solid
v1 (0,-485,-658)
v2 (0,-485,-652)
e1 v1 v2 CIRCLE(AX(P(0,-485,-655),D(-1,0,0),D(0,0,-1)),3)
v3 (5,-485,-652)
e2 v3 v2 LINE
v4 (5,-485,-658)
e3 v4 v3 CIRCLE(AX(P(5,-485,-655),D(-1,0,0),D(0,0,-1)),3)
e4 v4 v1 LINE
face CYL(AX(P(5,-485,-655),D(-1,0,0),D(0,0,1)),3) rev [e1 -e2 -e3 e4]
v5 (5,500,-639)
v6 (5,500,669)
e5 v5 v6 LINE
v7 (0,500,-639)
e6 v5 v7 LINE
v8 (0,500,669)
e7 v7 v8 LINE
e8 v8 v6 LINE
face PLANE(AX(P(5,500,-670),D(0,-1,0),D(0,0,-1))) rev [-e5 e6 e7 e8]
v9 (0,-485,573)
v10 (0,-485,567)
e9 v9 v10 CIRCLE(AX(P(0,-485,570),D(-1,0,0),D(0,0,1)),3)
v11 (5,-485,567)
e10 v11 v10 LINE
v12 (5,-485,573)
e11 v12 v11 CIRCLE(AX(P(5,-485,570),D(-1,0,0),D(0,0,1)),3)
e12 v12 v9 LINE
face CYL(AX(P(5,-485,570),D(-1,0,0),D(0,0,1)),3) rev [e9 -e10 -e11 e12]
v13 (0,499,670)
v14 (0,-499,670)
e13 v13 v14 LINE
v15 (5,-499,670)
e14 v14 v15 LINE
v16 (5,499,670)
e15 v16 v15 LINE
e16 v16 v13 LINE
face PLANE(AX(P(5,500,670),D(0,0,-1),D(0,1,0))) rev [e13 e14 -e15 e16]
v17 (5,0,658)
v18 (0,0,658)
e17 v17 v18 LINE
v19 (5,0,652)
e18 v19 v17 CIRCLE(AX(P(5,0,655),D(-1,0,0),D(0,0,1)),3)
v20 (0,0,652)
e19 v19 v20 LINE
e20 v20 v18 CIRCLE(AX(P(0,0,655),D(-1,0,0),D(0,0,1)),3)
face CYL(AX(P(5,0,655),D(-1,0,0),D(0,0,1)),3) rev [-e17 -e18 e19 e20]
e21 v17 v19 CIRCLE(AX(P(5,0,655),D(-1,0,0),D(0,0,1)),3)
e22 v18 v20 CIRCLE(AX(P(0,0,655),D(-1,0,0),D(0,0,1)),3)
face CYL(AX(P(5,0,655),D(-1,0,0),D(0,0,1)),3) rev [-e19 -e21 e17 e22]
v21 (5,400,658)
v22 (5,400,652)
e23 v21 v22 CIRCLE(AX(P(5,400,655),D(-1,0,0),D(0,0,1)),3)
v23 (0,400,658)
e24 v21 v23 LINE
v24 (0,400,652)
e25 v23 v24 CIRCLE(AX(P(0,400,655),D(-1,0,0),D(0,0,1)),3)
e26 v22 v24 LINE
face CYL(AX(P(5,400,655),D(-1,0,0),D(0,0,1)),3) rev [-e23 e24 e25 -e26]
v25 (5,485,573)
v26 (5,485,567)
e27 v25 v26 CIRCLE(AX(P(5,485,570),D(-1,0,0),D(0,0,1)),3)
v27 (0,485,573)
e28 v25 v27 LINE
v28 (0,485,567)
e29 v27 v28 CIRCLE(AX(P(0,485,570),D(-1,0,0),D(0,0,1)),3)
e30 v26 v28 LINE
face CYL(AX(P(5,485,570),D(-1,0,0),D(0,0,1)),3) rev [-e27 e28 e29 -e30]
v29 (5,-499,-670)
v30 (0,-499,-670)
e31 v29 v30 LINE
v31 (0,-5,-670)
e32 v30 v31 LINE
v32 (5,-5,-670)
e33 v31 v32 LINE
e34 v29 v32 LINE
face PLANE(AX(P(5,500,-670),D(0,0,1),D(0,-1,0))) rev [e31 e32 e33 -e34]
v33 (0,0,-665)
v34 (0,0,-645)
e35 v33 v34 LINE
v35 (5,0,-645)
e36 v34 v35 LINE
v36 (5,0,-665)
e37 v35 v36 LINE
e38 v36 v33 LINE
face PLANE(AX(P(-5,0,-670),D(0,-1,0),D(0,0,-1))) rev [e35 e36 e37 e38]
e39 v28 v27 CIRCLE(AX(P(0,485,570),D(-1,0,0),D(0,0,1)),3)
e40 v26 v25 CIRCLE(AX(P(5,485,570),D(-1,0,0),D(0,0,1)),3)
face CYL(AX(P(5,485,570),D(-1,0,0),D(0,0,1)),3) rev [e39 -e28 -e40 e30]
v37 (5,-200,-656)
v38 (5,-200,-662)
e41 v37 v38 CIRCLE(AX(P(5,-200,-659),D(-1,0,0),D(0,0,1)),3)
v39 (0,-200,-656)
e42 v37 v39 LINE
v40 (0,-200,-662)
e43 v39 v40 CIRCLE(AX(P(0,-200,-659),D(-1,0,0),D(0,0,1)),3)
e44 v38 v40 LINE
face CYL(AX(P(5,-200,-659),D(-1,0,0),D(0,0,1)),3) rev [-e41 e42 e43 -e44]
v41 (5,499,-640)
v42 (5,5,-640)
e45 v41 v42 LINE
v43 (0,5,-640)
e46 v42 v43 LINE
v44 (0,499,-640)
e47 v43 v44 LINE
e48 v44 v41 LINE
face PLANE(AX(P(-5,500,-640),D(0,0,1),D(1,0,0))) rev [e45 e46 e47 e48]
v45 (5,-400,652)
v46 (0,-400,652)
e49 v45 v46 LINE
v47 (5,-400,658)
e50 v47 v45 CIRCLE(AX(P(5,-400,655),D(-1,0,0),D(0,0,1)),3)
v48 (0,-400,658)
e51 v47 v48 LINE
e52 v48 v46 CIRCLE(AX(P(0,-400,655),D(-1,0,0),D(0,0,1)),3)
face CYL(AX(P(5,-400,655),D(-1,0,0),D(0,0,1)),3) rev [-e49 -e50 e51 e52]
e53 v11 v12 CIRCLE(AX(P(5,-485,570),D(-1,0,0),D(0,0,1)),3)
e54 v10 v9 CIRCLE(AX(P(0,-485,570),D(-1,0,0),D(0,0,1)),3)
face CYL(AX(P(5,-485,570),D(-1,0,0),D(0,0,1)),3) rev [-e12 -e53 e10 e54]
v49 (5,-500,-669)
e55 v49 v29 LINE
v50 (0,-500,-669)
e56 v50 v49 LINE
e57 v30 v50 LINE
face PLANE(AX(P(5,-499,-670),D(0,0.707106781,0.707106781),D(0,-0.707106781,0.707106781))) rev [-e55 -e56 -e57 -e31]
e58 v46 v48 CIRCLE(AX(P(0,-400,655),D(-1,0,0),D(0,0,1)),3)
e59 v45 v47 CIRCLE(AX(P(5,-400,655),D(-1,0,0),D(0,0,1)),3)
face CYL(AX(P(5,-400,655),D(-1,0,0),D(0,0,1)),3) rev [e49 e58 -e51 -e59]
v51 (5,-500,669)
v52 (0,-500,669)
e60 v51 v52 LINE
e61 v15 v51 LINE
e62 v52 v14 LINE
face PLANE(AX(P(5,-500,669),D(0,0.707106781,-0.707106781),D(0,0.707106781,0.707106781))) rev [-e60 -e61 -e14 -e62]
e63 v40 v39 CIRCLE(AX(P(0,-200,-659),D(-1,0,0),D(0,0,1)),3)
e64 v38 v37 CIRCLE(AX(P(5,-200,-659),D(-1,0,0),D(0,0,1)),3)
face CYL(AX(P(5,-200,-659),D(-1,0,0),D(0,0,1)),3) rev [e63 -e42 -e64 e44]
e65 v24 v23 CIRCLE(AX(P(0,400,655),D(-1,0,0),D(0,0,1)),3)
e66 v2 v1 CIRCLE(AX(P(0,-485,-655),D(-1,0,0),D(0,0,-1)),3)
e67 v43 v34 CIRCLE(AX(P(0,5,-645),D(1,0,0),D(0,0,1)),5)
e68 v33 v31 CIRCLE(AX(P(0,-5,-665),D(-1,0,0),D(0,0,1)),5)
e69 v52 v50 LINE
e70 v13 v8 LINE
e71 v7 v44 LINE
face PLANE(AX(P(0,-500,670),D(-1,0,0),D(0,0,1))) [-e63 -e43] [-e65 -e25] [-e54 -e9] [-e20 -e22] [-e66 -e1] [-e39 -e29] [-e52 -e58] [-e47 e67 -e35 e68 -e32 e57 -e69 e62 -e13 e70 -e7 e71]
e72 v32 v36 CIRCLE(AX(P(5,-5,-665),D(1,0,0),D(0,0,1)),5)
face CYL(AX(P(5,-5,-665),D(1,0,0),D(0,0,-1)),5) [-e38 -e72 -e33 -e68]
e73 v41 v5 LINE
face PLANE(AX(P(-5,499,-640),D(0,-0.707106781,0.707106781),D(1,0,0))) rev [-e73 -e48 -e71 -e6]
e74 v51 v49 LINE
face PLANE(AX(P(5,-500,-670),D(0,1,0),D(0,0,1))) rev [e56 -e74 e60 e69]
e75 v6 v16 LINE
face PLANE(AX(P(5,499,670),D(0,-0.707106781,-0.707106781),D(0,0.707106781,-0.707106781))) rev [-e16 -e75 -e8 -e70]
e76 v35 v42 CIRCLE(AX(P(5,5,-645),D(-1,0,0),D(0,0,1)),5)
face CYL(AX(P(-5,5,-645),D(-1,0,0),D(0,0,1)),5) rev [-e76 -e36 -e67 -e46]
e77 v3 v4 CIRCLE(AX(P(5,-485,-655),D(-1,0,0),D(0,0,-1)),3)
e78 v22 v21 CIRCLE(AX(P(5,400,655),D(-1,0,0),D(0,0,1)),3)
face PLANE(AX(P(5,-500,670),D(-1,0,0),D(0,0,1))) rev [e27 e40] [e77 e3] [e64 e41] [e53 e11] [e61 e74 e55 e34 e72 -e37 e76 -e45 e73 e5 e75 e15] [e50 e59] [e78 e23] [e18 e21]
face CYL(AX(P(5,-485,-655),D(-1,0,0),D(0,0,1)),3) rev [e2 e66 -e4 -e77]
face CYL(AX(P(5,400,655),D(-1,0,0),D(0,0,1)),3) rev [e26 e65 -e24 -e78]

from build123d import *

# Parameters (mm, degrees)
SKETCH_1_W          = 1340
SKETCH_1_H          = 1000
EXTRUDE_1_DEPTH     = 5
CHAMFER_1_SIZE      = 1
SKETCH_2_R          = 3
CUT_EXTRUDE_1_DEPTH = 837.017344318
SKETCH_3_W          = 30
SKETCH_3_H          = 500
CUT_EXTRUDE_2_DEPTH = 10
CHAMFER_2_SIZE      = 1
FILLET_1_R          = 5
FILLET_2_R          = 5


with BuildPart() as part:
    # 草图1 → 凸台-拉伸1 (new body)
    with BuildSketch(Plane(origin=(0, 0, 0), x_dir=(0, 0, -1), z_dir=(1, 0, 0))):
        Rectangle(SKETCH_1_W, SKETCH_1_H)
    extrude(amount=EXTRUDE_1_DEPTH)

    # 倒角1
    chamfer_1_edges = [part.edges().sort_by_distance(p)[0] for p in [
        (2.5, 500, 670),
        (2.5, 500, -670),
        (2.5, -500, -670),
        (2.5, -500, 670),
    ]]
    chamfer(chamfer_1_edges, length=CHAMFER_1_SIZE)

    # 草图2 → 切除-拉伸1 (cut, through all)
    with BuildSketch(Plane.ZY):
        with Locations((-655, 485)):
            Circle(SKETCH_2_R)
        with Locations(Location((-655, -485, 0), (0, 0, 180))):
            Circle(SKETCH_2_R)
        with Locations((570, 485)):
            Circle(SKETCH_2_R)
        with Locations((655, 400)):
            Circle(SKETCH_2_R)
        with Locations((655, -400)):
            Circle(SKETCH_2_R)
        with Locations((570, -485)):
            Circle(SKETCH_2_R)
        with Locations((655, 0)):
            Circle(SKETCH_2_R)
        with Locations((-659, 200)):
            Circle(SKETCH_2_R)
        with Locations((-659, -200)):
            Circle(SKETCH_2_R)
    extrude(amount=-CUT_EXTRUDE_1_DEPTH, mode=Mode.SUBTRACT)

    # 草图3 → 切除-拉伸2 (cut)
    with BuildSketch(Plane(origin=(5, 0, 0), x_dir=(0, 0, -1), z_dir=(1, 0, 0))):
        with Locations((655, 250)):
            Rectangle(SKETCH_3_W, SKETCH_3_H)
    extrude(amount=-CUT_EXTRUDE_2_DEPTH, mode=Mode.SUBTRACT)

    # 倒角2
    chamfer_2_edges = [part.edges().sort_by_distance(p)[0] for p in [
        (2.5, 500, -640),
    ]]
    chamfer(chamfer_2_edges, length=CHAMFER_2_SIZE)

    # 圆角1
    fillet_1_edges = [part.edges().sort_by_distance(p)[0] for p in [
        (2.5, 0, -640),
    ]]
    fillet(fillet_1_edges, radius=FILLET_1_R)

    # 圆角2
    fillet_2_edges = [part.edges().sort_by_distance(p)[0] for p in [
        (2.5, 0, -670),
    ]]
    fillet(fillet_2_edges, radius=FILLET_2_R)


solid = part.part
